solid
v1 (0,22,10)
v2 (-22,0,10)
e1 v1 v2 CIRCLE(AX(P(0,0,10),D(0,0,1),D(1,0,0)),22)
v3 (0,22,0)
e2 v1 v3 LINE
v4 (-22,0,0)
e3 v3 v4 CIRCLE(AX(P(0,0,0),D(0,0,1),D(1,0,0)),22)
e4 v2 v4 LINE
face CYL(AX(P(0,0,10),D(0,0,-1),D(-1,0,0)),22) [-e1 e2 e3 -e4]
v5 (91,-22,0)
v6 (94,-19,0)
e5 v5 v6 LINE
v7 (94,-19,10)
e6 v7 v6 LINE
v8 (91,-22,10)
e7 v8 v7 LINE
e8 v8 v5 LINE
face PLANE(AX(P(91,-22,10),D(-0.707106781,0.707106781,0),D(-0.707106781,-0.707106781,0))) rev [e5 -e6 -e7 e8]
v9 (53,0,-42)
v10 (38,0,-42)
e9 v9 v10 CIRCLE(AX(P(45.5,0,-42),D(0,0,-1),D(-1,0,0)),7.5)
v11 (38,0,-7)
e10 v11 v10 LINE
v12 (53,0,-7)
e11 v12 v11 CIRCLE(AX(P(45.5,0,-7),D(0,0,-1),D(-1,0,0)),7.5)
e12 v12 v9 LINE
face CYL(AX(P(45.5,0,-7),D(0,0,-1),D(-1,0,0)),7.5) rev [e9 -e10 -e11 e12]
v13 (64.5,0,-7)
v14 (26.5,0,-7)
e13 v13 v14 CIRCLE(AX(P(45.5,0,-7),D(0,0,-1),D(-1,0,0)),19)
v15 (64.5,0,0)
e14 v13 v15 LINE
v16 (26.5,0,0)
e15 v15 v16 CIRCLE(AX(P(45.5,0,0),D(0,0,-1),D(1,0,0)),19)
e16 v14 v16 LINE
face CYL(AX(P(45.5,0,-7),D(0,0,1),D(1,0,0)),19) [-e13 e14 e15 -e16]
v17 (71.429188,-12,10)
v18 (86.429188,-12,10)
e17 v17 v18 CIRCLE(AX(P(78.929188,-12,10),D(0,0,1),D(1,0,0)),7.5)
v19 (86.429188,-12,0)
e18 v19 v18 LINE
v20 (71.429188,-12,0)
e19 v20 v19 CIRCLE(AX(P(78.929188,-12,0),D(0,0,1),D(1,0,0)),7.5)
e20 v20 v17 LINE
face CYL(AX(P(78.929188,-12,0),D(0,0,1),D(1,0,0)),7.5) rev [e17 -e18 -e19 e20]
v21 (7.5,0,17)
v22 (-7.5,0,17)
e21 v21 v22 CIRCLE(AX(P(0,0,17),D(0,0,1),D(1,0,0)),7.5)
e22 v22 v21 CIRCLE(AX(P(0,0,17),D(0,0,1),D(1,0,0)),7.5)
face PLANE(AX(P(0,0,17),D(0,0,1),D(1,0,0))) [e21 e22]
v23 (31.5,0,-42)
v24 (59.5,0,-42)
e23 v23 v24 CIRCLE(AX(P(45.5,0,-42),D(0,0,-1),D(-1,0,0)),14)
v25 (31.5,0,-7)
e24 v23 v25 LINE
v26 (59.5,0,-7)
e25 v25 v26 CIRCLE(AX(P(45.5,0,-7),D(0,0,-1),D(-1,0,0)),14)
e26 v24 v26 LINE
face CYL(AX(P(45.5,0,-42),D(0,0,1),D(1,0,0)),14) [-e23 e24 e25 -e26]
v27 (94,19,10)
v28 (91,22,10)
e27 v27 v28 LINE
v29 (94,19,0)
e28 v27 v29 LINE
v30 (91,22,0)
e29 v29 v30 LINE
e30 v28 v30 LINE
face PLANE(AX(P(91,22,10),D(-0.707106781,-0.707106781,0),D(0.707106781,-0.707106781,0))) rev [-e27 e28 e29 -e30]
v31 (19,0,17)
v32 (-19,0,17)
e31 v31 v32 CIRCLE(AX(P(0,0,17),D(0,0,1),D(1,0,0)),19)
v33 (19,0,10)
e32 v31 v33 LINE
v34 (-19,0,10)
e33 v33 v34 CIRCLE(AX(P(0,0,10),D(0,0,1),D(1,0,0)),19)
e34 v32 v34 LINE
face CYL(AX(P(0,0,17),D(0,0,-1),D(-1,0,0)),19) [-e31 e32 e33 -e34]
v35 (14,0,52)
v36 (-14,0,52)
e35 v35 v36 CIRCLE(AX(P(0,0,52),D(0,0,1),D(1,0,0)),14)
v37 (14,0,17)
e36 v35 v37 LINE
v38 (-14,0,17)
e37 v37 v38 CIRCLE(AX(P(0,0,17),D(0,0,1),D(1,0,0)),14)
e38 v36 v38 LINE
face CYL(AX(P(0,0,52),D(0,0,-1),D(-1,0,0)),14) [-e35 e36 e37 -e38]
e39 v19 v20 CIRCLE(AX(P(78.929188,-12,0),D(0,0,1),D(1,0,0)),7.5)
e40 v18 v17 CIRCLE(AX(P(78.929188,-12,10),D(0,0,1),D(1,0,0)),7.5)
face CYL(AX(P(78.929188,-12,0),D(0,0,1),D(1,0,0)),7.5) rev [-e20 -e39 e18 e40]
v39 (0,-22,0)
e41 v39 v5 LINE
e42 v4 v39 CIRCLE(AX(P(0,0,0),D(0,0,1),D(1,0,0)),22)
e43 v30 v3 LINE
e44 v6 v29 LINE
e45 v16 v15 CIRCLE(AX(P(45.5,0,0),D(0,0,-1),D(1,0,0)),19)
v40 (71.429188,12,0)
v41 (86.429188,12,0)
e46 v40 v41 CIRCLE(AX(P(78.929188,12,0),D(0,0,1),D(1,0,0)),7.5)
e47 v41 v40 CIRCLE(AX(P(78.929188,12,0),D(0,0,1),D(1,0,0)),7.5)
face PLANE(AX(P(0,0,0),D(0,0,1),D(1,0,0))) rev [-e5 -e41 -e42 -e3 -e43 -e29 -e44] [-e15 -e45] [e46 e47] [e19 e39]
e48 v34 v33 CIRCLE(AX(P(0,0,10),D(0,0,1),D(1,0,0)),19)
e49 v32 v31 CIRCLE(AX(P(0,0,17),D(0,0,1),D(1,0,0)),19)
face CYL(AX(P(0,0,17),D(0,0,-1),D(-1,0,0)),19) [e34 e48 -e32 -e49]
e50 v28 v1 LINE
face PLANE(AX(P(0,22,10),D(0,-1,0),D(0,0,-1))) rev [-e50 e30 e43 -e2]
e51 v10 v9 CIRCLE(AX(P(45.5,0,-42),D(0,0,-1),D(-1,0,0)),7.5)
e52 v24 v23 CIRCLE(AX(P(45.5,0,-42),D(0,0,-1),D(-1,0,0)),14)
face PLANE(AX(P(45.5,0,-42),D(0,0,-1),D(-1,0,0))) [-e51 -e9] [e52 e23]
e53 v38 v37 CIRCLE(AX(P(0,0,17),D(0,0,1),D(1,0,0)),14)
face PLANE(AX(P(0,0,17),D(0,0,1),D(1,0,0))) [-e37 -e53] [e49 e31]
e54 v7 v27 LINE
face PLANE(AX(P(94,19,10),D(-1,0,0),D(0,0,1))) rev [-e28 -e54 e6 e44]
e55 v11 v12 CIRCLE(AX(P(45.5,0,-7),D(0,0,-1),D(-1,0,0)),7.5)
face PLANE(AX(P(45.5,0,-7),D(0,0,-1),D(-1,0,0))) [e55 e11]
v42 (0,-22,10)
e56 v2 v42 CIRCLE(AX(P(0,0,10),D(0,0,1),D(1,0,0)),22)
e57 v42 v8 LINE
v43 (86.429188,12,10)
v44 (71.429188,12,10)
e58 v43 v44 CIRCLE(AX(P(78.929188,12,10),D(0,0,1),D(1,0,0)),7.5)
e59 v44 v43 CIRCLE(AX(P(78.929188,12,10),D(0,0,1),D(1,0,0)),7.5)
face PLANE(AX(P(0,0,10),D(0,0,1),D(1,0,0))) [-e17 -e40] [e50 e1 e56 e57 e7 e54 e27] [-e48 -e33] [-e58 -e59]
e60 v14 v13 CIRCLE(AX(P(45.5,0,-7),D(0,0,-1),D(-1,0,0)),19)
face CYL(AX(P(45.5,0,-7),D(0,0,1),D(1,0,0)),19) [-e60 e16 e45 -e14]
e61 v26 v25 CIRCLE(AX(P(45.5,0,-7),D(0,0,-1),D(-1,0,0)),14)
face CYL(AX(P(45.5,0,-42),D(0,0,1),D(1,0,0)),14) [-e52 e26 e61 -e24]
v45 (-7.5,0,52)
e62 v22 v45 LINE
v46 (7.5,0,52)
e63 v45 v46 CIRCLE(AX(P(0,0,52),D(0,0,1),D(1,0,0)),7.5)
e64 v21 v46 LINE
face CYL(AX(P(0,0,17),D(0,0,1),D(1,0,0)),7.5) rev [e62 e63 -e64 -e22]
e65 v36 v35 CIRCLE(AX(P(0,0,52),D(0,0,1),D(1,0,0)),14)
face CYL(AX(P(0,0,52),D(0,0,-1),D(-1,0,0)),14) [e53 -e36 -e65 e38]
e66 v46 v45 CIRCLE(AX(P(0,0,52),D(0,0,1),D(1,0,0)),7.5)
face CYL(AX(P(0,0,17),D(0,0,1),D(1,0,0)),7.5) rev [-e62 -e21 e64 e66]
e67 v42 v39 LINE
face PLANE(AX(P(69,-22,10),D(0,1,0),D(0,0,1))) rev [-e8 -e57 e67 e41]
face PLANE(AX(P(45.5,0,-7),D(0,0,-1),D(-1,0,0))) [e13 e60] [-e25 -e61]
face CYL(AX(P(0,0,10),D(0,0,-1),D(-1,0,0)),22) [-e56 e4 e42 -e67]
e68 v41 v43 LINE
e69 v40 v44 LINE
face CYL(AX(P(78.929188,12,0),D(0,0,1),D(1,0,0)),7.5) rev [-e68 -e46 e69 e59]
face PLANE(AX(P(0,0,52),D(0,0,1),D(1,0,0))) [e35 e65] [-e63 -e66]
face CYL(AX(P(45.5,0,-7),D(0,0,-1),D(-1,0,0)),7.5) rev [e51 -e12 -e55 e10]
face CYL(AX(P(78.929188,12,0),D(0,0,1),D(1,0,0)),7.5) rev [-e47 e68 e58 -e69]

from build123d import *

# Parameters (mm, degrees)
BASE_PLATE_DEPTH      = 10
FRONT_COLLAR_SKETCH_R = 19
FRONT_COLLAR_38_DEPTH = 7
FRONT_SHAFT_SKETCH_R  = 14
FRONT_SHAFT_28_DEPTH  = 35
REAR_COLLAR_SKETCH_R  = 19
REAR_COLLAR_38_DEPTH  = 7
REAR_SHAFT_SKETCH_R   = 14
REAR_SHAFT_28_DEPTH   = 35
REAR_BORE_SKETCH_R    = 7.5
REAR_BORE_15_DEPTH    = 35
FRONT_BORE_SKETCH_R   = 7.5
FRONT_BORE_15_DEPTH   = 35
END_HOLES_SKETCH_R    = 7.5
END_HOLES_2X_15_DEPTH = 10


with BuildPart() as part:
    # Base Plate Sketch → Base Plate (new body)
    with BuildSketch(Plane.XY):
        with BuildLine():
            Line((0, 22), (69, 22))
            Line((69, 22), (91, 22))
            Line((91, 22), (94, 19))
            Line((94, 19), (94, -19))
            Line((94, -19), (91, -22))
            Line((91, -22), (69, -22))
            Line((69, -22), (0, -22))
            ThreePointArc((0, -22), (-22, 0), (0, 22))
        make_face()
    extrude(amount=BASE_PLATE_DEPTH)

    # Front Collar Sketch → Front Collar Ø38 (add)
    with BuildSketch(Plane.XY.offset(10)):
        Circle(FRONT_COLLAR_SKETCH_R)
    extrude(amount=FRONT_COLLAR_38_DEPTH)

    # Front Shaft Sketch → Front Shaft Ø28 (add)
    with BuildSketch(Plane.XY.offset(17)):
        Circle(FRONT_SHAFT_SKETCH_R)
    extrude(amount=FRONT_SHAFT_28_DEPTH)

    # Rear Collar Sketch → Rear Collar Ø38 (add)
    with BuildSketch(Plane(origin=(0, 0, 0), x_dir=(-1, 0, 0), z_dir=(0, 0, -1))):
        with Locations(Location((-45.5, 0, 0), (0, 0, 180))):
            Circle(REAR_COLLAR_SKETCH_R)
    extrude(amount=REAR_COLLAR_38_DEPTH)

    # Rear Shaft Sketch → Rear Shaft Ø28 (add)
    with BuildSketch(Plane(origin=(0, 0, -7), x_dir=(-1, 0, 0), z_dir=(0, 0, -1))):
        with Locations((-45.5, 0)):
            Circle(REAR_SHAFT_SKETCH_R)
    extrude(amount=REAR_SHAFT_28_DEPTH)

    # Rear Bore Sketch → Rear Bore Ø15 (cut)
    with BuildSketch(Plane(origin=(0, 0, -42), x_dir=(-1, 0, 0), z_dir=(0, 0, -1))):
        with Locations((-45.5, 0)):
            Circle(REAR_BORE_SKETCH_R)
    extrude(amount=-REAR_BORE_15_DEPTH, mode=Mode.SUBTRACT)

    # Front Bore Sketch → Front Bore Ø15 (cut)
    with BuildSketch(Plane.XY.offset(52)):
        Circle(FRONT_BORE_SKETCH_R)
    extrude(amount=-FRONT_BORE_15_DEPTH, mode=Mode.SUBTRACT)

    # End Holes Sketch → End Holes 2xØ15 (cut)
    with BuildSketch(Plane.XY.offset(10)):
        with Locations((78.929188111, 12)):
            Circle(END_HOLES_SKETCH_R)
        with Locations((78.929188111, -12)):
            Circle(END_HOLES_SKETCH_R)
    extrude(amount=-END_HOLES_2X_15_DEPTH, mode=Mode.SUBTRACT)


solid = part.part
